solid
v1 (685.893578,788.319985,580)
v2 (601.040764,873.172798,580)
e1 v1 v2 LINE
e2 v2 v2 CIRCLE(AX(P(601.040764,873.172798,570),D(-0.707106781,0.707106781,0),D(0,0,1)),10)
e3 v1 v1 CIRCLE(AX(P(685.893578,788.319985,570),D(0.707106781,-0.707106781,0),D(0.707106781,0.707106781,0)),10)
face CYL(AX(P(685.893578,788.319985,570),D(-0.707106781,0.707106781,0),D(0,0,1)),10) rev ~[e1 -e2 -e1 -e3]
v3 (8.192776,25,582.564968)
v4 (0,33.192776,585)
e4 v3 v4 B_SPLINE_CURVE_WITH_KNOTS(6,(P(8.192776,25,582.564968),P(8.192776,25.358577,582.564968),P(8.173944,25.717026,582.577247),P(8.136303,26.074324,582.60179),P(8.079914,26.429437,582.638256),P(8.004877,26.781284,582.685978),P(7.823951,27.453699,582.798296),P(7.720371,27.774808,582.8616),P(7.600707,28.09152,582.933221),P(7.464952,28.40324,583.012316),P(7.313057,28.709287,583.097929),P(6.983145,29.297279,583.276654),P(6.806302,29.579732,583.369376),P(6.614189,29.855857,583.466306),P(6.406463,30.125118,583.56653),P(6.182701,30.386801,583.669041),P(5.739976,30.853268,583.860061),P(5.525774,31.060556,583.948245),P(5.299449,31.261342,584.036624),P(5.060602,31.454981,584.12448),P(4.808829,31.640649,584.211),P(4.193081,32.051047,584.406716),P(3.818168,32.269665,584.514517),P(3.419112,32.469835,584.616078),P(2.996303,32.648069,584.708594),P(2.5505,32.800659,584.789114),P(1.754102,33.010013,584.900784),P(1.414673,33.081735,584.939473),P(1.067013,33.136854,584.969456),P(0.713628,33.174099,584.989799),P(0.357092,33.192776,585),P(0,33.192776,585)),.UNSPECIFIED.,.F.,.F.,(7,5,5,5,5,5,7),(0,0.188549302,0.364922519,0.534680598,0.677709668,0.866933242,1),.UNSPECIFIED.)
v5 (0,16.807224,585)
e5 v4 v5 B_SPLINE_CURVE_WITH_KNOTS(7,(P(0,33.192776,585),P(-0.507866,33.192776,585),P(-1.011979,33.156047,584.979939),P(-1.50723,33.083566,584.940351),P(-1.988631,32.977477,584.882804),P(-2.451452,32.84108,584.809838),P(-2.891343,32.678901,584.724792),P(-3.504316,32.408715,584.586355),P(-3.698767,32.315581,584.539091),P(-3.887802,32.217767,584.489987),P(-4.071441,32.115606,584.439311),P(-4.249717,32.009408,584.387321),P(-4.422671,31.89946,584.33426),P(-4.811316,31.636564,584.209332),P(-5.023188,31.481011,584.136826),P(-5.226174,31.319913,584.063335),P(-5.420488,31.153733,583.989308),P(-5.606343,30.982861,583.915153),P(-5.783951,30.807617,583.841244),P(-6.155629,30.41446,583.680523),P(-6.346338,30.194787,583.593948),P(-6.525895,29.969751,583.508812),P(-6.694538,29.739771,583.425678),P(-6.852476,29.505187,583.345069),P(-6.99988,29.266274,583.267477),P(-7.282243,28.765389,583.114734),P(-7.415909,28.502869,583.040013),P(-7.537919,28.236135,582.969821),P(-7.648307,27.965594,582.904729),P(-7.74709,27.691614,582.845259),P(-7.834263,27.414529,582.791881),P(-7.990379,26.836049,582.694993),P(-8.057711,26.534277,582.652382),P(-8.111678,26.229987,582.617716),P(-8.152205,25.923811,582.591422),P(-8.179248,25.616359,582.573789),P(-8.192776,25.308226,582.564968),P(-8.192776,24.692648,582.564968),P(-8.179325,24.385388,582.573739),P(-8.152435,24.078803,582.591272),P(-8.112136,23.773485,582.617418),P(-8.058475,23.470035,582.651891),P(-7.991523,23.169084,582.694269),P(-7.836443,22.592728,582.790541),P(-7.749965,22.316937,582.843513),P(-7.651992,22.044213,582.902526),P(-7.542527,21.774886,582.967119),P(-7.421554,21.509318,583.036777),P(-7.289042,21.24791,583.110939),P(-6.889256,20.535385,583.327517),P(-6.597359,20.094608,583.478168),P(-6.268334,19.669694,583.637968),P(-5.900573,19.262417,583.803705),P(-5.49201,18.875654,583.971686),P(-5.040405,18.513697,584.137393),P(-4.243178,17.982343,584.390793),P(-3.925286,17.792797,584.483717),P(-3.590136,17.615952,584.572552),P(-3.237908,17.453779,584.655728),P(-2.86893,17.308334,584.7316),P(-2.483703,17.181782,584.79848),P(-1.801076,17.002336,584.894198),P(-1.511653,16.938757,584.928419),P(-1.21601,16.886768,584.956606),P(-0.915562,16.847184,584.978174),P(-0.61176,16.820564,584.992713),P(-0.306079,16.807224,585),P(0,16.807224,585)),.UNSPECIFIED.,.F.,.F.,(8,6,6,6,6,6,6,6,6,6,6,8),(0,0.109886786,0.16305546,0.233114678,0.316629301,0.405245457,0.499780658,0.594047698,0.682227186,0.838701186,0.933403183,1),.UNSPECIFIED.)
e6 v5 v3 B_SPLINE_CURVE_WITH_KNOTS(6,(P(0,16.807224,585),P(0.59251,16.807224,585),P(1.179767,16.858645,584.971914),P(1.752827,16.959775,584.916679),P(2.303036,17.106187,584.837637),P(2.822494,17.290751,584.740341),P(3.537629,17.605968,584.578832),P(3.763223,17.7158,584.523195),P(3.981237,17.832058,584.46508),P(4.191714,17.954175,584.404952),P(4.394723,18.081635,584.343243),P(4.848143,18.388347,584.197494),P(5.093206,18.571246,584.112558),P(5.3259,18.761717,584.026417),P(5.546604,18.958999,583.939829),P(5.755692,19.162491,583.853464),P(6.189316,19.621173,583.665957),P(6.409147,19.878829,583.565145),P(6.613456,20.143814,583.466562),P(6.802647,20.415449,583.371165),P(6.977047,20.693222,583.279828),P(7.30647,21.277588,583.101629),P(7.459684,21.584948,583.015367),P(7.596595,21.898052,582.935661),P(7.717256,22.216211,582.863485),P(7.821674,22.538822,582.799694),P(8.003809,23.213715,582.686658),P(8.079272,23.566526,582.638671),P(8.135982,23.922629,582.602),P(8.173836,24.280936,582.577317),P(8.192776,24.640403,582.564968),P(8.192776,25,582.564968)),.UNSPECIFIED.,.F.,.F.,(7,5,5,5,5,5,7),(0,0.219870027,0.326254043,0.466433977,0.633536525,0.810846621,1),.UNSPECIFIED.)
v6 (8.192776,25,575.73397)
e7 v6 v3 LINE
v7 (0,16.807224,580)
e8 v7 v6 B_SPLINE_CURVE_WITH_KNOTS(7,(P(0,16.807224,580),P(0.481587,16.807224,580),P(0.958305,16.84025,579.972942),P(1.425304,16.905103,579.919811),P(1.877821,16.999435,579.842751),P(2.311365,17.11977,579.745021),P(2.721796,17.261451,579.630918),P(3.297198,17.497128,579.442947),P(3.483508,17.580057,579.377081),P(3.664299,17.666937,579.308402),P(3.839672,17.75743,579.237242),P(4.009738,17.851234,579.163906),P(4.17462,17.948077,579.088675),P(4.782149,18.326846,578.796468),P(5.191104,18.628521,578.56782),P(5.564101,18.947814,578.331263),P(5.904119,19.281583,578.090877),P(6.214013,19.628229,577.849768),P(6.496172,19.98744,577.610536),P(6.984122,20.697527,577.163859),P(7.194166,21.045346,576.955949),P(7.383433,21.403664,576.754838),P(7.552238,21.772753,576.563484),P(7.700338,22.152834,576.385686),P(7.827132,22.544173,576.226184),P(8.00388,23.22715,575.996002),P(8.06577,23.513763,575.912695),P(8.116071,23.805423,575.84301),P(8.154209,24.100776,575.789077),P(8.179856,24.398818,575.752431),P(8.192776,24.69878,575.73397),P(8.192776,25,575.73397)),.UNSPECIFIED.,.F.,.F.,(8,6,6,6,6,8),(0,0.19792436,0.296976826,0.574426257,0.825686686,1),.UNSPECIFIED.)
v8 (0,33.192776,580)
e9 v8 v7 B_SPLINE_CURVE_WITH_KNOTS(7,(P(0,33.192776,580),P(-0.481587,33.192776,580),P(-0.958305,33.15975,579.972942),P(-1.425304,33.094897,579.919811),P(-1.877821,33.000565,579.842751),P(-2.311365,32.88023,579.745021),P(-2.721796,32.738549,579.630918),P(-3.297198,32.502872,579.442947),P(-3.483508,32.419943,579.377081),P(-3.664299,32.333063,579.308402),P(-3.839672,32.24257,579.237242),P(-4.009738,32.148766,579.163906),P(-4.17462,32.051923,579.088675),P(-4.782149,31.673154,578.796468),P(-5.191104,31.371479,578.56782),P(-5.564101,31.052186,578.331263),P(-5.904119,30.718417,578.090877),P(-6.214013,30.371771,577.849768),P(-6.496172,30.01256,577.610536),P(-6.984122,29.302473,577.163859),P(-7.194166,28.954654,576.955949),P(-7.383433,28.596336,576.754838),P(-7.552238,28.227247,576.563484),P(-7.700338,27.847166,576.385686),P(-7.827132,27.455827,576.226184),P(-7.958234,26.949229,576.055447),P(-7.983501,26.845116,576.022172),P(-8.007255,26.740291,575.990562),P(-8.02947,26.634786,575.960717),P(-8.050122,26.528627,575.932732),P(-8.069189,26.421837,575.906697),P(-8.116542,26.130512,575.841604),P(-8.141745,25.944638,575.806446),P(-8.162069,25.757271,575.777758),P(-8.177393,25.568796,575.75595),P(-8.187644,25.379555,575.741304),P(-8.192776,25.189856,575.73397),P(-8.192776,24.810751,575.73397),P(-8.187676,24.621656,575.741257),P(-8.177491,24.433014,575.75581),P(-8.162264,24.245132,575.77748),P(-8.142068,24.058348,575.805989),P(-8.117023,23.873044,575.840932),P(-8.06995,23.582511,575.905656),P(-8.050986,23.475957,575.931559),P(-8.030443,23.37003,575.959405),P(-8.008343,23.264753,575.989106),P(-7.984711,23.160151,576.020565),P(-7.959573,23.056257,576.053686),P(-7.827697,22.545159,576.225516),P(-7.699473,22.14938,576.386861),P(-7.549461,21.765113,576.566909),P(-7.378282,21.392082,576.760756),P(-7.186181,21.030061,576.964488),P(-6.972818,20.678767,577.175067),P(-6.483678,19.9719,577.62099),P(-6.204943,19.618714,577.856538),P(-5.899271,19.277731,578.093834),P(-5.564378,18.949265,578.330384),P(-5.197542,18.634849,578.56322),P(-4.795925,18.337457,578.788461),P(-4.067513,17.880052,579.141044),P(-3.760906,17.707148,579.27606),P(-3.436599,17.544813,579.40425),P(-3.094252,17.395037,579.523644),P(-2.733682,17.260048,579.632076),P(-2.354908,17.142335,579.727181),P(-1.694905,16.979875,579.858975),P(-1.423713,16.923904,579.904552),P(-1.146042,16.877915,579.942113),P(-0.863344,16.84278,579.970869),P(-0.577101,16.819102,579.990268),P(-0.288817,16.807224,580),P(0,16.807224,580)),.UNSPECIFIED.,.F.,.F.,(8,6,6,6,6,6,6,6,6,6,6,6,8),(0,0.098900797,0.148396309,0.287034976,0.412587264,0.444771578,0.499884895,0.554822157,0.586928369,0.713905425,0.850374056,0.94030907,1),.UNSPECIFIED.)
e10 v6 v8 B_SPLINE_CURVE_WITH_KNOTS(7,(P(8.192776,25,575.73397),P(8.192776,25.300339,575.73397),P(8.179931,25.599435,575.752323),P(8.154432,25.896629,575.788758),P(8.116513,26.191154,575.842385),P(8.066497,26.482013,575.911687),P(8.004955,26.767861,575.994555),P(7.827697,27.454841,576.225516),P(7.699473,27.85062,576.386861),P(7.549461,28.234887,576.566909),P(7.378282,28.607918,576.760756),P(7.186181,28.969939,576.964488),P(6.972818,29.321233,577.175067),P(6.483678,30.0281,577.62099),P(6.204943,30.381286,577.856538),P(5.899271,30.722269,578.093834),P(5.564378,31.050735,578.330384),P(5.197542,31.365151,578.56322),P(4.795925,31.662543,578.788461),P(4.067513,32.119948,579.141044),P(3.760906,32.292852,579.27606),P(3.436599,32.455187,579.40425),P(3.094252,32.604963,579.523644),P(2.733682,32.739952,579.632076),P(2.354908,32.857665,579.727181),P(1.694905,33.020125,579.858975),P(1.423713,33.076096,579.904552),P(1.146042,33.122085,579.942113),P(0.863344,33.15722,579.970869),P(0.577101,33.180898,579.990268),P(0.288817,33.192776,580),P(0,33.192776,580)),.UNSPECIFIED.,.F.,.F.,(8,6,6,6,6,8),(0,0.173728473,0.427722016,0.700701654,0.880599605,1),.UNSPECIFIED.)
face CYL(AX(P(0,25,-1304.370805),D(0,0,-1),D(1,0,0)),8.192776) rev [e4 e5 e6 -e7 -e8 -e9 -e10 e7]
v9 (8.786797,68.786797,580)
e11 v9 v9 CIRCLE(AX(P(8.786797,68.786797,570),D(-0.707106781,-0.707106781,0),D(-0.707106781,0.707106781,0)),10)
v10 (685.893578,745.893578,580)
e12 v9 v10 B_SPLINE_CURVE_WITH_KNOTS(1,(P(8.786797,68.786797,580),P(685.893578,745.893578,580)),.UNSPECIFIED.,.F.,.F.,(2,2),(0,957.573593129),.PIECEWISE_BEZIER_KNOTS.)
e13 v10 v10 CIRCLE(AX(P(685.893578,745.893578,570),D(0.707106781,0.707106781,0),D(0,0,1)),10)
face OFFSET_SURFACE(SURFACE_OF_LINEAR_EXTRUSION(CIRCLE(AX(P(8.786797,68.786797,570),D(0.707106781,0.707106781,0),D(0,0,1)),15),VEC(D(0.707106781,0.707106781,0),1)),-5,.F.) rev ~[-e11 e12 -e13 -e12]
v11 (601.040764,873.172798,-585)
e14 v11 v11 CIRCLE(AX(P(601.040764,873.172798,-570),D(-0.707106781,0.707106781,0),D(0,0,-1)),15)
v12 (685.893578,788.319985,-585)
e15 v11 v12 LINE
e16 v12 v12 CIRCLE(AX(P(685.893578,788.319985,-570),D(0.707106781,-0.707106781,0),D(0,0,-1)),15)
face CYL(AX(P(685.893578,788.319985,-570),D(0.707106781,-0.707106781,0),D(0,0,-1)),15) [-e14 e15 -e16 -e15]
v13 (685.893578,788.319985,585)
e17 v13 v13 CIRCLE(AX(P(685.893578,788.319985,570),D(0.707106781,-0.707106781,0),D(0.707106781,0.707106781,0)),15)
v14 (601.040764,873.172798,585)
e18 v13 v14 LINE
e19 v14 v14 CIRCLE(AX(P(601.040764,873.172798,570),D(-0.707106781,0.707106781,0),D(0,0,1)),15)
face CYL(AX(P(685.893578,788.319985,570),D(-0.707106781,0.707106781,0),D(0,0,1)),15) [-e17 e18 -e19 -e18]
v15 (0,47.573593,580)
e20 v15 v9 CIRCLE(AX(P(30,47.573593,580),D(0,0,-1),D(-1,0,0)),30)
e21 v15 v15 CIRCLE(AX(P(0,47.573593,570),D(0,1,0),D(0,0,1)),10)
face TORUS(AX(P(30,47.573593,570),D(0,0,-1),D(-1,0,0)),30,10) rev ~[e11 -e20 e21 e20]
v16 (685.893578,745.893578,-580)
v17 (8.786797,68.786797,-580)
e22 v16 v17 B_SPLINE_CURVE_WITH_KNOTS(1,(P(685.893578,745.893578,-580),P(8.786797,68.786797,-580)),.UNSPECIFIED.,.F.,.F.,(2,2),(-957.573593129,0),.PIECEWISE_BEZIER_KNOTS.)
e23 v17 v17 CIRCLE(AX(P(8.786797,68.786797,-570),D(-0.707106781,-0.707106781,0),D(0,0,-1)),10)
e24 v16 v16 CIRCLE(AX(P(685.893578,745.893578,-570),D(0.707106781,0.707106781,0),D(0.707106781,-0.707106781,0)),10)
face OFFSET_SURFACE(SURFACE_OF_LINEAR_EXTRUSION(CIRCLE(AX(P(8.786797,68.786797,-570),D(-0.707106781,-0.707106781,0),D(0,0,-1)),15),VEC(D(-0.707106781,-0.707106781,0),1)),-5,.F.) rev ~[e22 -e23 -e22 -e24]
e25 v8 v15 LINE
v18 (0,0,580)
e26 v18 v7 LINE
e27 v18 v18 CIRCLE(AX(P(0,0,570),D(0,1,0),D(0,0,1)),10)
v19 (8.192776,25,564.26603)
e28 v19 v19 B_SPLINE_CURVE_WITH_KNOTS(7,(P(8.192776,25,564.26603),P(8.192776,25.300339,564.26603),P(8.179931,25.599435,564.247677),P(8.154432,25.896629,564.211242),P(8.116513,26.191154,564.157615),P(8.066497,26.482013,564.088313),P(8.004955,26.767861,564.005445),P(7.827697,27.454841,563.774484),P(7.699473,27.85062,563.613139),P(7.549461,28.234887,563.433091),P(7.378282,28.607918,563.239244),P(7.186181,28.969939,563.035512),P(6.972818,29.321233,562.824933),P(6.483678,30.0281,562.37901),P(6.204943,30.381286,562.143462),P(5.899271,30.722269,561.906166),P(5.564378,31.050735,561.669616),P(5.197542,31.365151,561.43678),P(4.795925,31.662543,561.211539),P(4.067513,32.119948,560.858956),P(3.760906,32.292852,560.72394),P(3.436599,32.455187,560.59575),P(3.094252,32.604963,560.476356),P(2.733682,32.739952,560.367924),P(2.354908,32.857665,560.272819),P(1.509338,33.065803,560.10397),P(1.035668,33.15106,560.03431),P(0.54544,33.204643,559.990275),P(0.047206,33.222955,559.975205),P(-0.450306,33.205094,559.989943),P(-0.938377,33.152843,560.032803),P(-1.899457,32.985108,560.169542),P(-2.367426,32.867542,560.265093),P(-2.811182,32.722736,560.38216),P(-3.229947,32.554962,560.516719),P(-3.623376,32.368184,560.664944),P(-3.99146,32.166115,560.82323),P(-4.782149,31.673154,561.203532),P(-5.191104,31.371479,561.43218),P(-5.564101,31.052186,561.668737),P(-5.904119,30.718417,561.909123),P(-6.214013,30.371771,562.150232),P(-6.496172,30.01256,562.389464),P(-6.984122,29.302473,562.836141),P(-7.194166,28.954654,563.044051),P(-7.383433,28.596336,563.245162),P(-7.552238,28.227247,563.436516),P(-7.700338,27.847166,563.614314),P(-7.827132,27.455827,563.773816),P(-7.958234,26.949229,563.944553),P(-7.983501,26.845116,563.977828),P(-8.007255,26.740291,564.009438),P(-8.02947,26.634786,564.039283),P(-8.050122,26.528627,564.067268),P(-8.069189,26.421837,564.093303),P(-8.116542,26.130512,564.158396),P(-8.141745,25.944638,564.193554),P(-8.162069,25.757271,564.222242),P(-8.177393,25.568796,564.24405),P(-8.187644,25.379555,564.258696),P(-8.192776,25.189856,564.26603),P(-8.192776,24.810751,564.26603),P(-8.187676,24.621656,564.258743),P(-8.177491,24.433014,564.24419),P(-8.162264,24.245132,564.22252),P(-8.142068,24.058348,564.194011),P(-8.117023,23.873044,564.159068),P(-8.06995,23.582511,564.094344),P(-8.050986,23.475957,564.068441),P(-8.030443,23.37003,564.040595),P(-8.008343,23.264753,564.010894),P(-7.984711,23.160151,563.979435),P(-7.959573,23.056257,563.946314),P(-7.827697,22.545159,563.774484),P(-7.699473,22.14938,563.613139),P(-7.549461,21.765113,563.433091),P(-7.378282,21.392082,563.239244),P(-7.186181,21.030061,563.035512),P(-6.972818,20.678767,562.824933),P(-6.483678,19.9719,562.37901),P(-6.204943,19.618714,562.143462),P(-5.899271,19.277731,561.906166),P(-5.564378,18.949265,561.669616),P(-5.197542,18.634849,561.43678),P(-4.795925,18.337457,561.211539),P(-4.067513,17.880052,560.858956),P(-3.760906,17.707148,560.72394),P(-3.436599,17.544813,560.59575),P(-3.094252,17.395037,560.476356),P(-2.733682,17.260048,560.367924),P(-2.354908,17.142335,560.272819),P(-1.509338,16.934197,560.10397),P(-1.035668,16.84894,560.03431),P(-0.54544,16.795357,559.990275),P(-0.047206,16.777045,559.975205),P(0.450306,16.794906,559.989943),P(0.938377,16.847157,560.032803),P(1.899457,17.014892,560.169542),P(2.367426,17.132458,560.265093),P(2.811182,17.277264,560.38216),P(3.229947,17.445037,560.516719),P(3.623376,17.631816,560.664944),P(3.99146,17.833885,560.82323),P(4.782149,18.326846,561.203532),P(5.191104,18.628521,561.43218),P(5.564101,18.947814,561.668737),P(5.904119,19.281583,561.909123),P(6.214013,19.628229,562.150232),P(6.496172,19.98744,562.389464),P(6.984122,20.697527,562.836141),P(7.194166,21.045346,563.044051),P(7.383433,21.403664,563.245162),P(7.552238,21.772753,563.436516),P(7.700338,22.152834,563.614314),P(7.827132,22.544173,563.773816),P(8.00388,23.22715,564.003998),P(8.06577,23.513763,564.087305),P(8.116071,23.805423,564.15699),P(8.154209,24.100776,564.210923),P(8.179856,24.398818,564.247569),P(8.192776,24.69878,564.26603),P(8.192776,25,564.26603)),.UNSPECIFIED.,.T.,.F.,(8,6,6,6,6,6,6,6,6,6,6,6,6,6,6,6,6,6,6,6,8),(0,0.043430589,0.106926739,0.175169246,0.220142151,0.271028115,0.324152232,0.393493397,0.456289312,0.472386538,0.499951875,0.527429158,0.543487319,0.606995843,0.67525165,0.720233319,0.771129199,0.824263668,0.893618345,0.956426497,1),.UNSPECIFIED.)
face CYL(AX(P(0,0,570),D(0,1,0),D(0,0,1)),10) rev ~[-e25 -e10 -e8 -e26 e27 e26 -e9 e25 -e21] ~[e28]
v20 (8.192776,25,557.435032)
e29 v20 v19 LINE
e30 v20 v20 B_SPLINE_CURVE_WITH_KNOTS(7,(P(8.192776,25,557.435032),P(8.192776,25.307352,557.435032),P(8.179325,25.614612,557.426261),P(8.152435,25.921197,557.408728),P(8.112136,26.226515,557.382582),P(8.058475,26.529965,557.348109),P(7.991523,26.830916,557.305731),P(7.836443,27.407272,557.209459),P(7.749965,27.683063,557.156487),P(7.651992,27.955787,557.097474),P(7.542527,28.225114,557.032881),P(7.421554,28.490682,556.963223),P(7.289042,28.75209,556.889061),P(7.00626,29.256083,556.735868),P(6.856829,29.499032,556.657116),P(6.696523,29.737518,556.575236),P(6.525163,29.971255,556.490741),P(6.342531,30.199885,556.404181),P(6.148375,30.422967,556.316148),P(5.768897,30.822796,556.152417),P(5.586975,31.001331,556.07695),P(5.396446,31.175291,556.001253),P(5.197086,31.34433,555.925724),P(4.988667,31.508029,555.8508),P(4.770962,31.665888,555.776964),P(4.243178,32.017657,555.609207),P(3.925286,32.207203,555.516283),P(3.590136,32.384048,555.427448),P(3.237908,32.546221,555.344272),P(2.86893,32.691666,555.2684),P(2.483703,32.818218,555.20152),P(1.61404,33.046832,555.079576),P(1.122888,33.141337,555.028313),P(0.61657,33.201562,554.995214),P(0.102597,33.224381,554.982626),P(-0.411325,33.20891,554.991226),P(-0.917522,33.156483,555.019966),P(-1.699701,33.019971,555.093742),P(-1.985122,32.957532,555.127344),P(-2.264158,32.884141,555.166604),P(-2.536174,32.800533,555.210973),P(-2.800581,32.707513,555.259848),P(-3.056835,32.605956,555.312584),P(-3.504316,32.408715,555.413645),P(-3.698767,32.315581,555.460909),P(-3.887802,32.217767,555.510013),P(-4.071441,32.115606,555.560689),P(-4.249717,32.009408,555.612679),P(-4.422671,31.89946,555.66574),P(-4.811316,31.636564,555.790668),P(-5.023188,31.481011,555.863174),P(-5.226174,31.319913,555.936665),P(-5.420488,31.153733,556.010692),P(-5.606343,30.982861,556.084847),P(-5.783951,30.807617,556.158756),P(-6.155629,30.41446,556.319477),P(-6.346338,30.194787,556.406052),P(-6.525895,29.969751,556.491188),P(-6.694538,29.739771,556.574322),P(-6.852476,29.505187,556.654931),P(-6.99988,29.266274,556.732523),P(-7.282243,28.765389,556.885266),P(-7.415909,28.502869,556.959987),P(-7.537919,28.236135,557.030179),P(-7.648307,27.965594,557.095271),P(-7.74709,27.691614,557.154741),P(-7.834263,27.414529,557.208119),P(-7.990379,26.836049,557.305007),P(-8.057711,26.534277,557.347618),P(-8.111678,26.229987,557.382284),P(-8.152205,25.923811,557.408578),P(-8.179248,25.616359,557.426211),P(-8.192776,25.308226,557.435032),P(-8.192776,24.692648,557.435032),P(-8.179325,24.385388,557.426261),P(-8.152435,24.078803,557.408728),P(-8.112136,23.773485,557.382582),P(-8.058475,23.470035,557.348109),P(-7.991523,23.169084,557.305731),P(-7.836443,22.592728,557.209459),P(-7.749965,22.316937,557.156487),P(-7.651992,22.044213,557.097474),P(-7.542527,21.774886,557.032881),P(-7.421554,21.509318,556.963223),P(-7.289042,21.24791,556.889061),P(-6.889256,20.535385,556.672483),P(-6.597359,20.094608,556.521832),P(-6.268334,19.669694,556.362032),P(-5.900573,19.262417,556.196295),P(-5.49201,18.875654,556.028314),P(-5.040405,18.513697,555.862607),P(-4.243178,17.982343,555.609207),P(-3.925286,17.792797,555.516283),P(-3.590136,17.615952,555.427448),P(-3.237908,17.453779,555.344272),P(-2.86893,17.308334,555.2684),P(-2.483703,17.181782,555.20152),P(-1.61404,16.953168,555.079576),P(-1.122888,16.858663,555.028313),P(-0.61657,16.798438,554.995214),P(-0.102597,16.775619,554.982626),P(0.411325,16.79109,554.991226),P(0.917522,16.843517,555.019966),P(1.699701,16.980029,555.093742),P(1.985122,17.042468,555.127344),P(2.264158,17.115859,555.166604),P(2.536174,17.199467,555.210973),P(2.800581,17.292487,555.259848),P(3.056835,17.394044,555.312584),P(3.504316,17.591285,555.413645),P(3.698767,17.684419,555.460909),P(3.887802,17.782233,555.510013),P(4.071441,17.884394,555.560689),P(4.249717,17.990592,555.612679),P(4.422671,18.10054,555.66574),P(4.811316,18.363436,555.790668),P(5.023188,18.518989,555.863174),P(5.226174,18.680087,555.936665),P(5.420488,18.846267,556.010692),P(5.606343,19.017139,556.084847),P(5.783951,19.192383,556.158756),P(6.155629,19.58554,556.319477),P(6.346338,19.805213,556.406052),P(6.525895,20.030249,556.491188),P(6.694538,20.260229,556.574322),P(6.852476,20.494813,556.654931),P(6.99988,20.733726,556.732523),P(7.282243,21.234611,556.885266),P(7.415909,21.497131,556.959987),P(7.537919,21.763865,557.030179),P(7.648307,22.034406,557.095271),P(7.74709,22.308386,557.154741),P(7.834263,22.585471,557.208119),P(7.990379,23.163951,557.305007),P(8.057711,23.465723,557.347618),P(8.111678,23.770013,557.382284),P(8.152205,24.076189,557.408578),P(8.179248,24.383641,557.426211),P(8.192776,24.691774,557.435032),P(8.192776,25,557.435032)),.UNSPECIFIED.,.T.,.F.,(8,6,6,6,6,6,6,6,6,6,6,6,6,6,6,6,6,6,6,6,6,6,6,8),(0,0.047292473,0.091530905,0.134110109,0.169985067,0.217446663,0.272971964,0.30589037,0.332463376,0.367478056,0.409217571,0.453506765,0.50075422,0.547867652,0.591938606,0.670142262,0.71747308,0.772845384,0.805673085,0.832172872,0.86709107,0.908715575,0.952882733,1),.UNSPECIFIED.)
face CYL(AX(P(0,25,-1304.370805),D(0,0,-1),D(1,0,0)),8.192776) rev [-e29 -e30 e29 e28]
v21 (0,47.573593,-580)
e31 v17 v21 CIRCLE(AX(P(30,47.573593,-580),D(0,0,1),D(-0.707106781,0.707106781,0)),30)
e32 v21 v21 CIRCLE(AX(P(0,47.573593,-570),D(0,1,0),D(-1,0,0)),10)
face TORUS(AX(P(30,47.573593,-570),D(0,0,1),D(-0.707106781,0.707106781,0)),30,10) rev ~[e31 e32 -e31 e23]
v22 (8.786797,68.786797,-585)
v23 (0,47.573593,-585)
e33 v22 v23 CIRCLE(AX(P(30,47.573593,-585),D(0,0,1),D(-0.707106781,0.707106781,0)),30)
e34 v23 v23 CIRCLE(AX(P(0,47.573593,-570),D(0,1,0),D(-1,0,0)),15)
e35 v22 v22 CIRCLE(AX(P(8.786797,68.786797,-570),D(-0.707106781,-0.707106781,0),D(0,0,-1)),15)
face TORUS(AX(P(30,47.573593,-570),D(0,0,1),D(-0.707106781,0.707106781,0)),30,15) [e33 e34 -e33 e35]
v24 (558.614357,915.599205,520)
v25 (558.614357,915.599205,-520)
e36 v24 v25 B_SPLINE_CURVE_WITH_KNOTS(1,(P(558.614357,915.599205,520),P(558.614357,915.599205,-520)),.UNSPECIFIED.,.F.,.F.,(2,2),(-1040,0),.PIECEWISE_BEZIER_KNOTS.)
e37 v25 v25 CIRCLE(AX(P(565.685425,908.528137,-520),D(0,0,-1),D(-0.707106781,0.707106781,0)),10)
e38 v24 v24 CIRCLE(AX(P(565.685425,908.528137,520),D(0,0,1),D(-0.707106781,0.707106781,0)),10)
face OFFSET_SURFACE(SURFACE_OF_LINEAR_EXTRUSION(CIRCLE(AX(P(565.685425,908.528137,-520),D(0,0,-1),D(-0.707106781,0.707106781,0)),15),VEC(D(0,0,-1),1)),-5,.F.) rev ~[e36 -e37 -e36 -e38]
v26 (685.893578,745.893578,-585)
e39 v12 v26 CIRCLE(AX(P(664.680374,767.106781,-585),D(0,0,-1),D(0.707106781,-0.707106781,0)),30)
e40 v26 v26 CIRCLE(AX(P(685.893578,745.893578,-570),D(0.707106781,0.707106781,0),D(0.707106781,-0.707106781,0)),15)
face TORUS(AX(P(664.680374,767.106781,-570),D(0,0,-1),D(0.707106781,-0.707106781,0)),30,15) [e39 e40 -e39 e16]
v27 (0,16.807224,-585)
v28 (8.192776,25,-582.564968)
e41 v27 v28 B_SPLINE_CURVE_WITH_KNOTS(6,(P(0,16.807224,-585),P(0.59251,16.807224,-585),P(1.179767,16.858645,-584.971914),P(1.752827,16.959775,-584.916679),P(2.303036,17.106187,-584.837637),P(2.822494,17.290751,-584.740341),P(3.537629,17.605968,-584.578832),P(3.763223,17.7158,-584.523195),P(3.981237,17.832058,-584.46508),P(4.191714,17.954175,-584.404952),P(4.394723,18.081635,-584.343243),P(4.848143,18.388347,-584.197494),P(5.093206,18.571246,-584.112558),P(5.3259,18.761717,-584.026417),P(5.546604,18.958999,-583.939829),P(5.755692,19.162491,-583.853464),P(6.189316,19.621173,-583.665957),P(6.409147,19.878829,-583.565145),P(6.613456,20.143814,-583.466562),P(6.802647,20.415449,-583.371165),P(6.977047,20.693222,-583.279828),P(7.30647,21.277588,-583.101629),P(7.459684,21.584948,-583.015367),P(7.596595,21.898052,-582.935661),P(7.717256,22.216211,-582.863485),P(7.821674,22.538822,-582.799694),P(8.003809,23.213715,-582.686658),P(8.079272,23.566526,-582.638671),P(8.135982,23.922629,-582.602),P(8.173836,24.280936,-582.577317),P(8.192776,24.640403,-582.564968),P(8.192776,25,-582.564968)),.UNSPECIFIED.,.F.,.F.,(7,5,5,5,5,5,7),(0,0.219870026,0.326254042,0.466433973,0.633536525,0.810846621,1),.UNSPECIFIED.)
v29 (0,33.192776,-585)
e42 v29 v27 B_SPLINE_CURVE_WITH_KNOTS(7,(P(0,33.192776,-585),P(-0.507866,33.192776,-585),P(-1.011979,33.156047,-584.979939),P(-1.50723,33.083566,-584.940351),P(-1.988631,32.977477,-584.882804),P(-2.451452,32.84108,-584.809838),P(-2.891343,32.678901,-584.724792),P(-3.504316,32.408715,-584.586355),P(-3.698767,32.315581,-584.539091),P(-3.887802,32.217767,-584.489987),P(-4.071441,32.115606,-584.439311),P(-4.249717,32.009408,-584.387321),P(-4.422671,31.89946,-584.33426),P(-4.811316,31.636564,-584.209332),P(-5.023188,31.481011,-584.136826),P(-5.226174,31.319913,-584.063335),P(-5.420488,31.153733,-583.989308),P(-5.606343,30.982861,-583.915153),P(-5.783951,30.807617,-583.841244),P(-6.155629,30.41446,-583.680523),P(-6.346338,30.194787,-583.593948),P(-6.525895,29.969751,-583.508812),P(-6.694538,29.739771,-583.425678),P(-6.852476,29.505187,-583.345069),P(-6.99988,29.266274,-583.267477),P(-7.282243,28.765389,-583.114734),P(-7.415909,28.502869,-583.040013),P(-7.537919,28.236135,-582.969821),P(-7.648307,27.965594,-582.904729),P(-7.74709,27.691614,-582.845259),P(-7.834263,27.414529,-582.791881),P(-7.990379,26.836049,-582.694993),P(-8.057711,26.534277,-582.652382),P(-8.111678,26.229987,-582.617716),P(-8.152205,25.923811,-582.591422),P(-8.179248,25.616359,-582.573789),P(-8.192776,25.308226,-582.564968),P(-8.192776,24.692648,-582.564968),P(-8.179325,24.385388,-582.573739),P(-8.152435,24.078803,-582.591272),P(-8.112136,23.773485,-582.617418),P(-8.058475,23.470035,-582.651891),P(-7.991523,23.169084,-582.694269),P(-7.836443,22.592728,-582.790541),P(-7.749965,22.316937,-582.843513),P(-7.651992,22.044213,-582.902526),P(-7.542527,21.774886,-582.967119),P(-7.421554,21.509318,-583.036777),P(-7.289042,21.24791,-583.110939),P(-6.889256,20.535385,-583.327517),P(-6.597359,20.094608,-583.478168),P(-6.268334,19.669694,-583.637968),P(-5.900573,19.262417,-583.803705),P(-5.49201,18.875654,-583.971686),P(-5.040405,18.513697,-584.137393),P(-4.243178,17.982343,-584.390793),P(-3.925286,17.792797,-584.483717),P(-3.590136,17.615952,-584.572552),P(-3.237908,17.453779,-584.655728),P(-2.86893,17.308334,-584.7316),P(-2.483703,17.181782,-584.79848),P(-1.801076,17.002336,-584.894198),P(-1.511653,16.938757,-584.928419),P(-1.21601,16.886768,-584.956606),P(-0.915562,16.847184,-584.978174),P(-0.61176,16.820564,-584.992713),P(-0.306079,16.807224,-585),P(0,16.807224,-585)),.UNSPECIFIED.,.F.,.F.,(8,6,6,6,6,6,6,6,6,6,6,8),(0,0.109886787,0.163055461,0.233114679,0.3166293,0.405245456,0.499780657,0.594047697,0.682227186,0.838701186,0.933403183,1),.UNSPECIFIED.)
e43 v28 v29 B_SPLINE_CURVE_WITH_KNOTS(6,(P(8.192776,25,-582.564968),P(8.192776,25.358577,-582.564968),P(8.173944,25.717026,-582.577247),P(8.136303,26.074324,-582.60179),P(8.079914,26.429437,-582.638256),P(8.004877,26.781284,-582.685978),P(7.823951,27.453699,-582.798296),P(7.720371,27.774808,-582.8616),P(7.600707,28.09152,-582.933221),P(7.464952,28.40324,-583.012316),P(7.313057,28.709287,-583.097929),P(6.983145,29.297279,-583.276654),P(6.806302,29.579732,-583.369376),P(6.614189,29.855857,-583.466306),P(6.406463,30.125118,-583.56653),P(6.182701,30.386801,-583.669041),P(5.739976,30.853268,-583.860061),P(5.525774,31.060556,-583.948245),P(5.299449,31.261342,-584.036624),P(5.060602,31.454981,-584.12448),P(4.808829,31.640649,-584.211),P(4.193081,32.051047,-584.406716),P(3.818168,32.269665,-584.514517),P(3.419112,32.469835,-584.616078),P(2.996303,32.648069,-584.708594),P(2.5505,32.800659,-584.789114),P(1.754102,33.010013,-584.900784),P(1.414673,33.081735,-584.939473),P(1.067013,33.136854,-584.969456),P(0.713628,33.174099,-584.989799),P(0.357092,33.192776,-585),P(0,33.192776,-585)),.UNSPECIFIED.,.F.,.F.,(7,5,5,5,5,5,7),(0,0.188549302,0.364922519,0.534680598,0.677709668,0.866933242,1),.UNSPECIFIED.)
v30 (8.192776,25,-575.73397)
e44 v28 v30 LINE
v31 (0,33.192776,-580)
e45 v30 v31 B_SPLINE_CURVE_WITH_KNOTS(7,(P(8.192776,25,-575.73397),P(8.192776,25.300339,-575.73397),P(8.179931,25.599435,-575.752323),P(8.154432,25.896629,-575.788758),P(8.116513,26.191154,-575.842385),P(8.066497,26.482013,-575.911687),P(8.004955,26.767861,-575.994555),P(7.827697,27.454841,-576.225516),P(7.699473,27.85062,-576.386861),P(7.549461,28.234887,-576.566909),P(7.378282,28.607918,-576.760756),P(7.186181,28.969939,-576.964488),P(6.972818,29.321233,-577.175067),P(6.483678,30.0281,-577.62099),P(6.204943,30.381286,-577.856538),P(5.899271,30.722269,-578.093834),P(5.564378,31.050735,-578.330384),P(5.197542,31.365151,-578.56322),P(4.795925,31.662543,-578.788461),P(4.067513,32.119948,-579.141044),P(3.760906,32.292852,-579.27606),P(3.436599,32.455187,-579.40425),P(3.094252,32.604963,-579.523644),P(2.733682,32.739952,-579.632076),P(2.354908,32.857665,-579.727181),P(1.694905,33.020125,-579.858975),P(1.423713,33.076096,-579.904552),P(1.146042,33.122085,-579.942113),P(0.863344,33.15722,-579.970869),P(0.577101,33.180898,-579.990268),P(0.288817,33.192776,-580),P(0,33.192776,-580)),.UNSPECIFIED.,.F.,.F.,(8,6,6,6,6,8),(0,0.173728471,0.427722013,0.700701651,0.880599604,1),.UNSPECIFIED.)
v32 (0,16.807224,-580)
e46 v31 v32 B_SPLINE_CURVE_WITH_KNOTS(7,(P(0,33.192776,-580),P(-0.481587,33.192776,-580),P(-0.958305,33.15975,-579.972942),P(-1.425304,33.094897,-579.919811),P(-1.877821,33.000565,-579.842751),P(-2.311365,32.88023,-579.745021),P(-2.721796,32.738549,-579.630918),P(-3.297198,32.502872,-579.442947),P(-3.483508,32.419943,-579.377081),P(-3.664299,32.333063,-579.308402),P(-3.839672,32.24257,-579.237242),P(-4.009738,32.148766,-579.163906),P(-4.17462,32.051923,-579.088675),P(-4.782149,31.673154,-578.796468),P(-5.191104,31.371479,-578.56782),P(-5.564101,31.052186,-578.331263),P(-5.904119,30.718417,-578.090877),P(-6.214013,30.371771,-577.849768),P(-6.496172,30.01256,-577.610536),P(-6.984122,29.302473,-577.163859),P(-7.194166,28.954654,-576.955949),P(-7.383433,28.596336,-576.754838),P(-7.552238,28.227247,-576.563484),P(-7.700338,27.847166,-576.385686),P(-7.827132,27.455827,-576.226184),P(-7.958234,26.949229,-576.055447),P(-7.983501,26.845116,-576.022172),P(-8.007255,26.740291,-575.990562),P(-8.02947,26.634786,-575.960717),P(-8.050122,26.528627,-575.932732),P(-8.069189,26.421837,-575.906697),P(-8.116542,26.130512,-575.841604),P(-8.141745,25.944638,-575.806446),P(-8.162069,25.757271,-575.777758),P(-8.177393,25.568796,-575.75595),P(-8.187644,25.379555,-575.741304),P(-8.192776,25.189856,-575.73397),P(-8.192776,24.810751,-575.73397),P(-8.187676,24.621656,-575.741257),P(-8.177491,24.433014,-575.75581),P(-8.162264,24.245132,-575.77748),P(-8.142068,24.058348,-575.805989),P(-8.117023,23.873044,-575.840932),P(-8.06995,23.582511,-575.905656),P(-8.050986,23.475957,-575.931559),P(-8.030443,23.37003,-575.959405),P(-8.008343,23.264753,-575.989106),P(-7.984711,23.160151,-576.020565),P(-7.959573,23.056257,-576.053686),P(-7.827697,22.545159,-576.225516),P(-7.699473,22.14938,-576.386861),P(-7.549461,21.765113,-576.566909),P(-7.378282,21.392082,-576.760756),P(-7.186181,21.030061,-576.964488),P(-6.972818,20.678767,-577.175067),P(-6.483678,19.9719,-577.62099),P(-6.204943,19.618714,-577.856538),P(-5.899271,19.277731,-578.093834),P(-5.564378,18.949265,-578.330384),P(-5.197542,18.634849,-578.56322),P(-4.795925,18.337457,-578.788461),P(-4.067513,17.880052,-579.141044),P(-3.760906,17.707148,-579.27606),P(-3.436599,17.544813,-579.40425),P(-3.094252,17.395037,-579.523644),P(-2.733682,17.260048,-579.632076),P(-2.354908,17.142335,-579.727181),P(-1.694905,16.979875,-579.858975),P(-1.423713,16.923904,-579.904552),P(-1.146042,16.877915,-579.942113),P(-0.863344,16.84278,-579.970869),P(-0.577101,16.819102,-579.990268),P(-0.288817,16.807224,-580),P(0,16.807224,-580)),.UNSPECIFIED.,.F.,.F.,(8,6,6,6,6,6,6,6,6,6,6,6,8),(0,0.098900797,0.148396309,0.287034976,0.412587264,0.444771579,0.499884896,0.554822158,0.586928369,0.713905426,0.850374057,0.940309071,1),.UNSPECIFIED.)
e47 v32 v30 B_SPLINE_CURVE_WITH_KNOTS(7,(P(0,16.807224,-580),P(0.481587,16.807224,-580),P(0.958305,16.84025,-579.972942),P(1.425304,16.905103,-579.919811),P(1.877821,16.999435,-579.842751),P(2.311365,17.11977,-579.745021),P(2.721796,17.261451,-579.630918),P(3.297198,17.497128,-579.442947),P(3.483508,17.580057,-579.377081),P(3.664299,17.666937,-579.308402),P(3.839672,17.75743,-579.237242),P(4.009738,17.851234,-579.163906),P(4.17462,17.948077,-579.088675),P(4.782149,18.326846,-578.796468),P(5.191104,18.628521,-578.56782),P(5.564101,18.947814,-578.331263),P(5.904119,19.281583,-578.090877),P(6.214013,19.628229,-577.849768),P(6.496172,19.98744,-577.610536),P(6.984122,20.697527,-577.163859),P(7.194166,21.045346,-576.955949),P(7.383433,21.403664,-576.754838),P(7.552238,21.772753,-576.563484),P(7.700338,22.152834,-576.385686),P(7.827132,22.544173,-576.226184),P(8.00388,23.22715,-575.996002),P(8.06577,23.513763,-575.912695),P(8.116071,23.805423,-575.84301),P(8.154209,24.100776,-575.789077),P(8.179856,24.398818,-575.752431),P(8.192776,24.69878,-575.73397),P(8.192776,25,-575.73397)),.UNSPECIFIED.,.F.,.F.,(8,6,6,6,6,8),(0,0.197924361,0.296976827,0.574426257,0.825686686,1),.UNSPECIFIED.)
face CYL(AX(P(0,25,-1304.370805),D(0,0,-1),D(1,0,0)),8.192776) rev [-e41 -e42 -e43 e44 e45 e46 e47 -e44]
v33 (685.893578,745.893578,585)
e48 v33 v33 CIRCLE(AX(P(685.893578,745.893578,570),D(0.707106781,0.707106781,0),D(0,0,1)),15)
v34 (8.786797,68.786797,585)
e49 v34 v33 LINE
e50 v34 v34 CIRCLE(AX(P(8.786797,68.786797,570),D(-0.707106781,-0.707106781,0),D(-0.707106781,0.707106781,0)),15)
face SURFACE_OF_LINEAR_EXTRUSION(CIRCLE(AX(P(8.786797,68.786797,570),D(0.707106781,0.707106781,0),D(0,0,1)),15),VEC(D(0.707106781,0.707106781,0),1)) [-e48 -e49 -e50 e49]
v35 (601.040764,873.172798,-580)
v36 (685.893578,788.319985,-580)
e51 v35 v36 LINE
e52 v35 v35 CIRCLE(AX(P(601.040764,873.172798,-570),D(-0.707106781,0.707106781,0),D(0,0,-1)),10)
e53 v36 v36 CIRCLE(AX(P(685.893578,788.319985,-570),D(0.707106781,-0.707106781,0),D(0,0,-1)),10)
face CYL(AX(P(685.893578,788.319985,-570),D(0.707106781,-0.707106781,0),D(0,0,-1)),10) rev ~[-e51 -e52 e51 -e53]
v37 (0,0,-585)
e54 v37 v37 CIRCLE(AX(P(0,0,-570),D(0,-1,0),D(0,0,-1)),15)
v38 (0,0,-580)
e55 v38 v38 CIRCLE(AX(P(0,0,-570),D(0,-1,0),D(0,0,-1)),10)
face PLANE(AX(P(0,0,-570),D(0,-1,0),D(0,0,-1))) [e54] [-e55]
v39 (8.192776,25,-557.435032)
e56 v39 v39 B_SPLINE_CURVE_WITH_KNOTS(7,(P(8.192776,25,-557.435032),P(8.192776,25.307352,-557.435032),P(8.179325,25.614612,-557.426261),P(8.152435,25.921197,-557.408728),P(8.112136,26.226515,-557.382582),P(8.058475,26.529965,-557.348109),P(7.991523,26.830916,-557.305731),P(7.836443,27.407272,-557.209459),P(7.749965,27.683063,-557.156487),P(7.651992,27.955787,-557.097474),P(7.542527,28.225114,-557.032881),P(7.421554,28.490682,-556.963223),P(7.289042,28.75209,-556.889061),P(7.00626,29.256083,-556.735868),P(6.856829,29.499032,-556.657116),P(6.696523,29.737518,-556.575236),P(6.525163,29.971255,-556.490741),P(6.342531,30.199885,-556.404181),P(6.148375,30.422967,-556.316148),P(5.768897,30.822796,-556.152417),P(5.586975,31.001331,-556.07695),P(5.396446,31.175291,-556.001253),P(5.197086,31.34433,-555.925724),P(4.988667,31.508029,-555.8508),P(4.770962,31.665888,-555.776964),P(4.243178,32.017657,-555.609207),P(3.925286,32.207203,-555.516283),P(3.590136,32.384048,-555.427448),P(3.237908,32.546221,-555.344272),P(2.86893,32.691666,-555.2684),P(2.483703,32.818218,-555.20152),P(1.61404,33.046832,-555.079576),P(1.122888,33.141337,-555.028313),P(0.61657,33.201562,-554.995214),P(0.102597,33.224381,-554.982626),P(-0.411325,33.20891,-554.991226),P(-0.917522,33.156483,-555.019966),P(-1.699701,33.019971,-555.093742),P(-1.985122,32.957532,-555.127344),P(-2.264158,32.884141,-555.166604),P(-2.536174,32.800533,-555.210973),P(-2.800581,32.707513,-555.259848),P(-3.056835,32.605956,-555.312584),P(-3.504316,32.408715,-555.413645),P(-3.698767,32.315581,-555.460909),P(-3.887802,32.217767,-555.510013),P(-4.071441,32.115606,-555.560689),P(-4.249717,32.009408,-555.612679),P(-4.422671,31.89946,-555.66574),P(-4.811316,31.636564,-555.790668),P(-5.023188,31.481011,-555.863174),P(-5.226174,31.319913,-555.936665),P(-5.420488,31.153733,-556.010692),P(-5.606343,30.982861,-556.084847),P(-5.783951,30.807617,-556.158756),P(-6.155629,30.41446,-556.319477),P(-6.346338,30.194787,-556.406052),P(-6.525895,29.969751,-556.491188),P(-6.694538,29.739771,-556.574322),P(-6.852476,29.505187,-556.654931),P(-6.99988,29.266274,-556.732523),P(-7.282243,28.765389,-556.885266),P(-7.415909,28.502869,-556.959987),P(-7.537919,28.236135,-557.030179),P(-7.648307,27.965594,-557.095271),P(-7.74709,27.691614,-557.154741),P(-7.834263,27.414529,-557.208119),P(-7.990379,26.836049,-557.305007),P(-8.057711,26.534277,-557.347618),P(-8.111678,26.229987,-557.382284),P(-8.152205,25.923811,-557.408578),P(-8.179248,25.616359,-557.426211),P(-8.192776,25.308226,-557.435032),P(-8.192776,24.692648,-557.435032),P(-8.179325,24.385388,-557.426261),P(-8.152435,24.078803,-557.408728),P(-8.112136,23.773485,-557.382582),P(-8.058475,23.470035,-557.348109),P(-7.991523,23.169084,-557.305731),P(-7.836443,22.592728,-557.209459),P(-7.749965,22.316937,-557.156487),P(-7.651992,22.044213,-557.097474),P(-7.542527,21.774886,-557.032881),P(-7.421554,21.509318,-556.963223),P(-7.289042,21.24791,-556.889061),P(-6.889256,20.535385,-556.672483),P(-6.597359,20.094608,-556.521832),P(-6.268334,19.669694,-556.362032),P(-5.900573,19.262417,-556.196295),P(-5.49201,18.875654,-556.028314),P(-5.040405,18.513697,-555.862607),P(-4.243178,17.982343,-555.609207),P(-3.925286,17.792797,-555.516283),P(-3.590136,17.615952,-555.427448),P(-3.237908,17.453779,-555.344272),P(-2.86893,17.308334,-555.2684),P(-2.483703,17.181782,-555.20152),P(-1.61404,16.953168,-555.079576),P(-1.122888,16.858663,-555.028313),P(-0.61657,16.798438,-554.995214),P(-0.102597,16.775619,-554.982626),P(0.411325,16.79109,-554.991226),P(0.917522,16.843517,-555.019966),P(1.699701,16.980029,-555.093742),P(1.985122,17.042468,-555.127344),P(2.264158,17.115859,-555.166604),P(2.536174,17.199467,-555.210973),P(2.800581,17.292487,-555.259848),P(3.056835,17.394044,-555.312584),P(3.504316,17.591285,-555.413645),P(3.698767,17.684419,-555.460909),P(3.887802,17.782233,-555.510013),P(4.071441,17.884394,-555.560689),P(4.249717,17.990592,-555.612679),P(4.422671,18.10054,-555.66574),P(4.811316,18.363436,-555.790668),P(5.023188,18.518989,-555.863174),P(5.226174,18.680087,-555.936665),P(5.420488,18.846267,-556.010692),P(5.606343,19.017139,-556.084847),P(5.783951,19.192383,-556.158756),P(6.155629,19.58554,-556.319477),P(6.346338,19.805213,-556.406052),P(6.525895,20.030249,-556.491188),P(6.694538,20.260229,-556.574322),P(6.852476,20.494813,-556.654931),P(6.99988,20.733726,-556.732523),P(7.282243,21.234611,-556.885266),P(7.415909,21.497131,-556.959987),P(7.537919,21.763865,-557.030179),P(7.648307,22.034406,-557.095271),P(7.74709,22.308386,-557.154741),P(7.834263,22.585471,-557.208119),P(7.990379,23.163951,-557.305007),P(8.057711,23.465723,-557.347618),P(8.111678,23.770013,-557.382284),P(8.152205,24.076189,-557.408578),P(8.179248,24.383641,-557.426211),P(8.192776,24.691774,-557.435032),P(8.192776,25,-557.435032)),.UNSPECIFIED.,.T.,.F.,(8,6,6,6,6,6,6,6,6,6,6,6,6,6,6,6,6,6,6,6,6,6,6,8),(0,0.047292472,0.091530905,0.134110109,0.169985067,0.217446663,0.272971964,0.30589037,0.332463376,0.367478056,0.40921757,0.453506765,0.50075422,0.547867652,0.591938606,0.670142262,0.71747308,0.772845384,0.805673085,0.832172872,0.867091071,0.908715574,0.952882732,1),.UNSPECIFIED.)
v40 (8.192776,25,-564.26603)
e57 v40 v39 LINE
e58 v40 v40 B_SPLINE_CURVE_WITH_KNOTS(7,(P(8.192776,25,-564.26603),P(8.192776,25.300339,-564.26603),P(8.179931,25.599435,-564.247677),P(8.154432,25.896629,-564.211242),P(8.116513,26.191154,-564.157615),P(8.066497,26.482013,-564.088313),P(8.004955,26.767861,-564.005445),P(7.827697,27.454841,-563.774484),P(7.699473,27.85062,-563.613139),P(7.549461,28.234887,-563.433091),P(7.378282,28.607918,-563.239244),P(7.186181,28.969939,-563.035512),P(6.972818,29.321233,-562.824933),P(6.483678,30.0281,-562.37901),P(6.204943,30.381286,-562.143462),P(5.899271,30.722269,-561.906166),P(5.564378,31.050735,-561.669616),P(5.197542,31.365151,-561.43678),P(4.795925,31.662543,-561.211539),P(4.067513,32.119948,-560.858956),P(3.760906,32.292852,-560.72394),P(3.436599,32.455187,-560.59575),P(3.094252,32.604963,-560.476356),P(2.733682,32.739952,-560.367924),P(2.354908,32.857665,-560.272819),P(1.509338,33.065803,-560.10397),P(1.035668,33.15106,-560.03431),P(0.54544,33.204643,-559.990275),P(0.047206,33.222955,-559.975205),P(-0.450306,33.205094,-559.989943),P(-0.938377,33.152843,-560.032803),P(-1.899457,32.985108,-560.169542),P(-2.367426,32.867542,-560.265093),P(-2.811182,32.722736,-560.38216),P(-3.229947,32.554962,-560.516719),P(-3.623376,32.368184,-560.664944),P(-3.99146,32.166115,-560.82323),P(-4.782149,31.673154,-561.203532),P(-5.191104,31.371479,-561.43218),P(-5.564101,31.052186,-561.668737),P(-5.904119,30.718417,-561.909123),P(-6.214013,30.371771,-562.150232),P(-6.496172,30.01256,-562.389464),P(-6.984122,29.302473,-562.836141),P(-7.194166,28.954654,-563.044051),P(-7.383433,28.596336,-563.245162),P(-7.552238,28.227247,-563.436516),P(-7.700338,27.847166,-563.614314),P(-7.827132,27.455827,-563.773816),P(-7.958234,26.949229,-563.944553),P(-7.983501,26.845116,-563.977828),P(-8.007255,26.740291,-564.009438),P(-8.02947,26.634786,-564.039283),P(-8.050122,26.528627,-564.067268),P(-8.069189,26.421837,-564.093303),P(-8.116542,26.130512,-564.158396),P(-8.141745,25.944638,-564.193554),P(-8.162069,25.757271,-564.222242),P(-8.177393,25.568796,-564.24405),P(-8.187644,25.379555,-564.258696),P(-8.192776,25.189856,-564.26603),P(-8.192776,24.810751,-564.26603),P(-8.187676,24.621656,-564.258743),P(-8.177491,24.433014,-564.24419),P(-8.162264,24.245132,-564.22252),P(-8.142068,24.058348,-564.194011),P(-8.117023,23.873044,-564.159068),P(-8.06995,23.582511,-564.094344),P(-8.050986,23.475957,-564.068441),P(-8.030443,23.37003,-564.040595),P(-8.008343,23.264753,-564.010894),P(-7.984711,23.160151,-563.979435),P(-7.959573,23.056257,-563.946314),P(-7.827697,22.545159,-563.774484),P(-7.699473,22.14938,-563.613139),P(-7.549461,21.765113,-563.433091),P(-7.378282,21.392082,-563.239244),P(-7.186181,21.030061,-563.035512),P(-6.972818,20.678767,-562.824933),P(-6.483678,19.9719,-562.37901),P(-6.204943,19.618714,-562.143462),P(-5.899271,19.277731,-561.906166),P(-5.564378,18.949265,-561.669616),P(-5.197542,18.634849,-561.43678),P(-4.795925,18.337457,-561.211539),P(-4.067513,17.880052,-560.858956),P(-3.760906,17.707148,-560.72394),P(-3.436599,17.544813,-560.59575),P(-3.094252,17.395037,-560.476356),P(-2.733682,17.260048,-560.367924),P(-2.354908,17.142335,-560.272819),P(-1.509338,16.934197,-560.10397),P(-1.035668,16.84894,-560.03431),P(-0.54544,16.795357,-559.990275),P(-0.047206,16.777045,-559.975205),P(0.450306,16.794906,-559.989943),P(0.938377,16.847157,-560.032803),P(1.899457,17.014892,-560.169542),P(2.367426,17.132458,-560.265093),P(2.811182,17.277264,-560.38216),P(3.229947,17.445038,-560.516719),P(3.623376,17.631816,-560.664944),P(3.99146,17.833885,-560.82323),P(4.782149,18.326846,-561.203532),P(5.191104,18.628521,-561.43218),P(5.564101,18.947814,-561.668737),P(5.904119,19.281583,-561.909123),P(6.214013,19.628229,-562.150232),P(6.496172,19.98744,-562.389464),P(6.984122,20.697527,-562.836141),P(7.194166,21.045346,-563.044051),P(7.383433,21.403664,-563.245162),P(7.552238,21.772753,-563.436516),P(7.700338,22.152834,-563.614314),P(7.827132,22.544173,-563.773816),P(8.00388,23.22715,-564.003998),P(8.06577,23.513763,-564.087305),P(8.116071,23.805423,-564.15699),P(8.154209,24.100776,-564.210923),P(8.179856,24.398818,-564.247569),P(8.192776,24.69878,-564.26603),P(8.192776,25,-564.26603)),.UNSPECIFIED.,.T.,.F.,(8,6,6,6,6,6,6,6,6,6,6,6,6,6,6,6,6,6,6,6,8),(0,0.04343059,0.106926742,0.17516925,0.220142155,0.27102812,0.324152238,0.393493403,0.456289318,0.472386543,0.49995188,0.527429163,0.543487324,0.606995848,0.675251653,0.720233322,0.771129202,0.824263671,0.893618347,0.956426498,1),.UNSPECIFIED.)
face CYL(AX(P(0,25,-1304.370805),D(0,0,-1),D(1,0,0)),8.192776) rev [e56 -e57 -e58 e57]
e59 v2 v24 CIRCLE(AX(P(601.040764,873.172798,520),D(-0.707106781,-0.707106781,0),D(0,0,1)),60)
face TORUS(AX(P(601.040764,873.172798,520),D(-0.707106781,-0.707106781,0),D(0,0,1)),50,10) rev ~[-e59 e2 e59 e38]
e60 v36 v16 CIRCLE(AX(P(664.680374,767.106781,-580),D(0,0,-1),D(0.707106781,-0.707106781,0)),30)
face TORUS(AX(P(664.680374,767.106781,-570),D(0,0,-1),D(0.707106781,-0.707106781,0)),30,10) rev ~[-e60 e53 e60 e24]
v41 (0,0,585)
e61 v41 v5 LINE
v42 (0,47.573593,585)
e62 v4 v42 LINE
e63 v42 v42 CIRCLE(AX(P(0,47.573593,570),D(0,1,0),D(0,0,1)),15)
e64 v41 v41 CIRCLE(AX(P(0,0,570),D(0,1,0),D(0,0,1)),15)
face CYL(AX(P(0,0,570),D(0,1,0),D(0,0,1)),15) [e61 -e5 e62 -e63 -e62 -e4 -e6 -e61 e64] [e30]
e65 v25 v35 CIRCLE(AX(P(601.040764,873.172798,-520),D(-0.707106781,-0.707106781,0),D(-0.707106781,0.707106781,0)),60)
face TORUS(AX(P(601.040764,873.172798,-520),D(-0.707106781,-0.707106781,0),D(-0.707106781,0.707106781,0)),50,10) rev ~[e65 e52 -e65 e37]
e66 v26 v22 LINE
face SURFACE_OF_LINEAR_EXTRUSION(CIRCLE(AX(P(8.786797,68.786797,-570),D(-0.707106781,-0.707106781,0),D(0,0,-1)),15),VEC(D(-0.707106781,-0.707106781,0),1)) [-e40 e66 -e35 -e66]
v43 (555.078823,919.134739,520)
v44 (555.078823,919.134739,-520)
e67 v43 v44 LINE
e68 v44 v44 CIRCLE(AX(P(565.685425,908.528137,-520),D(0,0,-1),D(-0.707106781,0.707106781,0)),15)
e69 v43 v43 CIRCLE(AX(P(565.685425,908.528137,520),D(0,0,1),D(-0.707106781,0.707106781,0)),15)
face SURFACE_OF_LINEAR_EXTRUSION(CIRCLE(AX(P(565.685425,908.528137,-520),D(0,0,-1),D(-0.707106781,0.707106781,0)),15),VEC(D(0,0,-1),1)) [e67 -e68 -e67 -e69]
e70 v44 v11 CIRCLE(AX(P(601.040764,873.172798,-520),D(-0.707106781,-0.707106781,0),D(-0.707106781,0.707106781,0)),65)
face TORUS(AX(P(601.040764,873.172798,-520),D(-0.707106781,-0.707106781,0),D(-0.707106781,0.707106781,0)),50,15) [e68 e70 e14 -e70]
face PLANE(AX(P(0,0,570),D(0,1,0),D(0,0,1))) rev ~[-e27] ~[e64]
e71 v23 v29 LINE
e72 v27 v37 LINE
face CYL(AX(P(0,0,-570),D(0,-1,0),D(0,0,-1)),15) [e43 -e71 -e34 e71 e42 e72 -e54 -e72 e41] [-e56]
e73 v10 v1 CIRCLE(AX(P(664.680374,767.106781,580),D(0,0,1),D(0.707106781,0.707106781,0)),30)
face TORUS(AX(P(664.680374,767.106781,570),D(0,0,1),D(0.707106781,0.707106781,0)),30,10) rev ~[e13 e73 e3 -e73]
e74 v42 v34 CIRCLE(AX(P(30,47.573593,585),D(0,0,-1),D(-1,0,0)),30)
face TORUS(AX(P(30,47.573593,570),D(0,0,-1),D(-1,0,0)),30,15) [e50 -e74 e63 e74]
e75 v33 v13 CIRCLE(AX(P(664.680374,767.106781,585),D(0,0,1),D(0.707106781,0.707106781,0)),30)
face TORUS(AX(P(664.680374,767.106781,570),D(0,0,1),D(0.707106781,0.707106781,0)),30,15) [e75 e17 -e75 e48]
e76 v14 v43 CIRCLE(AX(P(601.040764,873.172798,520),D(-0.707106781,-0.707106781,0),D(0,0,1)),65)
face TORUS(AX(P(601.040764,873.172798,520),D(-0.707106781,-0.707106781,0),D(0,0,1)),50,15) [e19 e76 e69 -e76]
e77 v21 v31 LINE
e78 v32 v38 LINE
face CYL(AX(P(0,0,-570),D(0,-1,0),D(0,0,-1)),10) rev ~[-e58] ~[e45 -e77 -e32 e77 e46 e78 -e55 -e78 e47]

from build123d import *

# Parameters (mm, degrees)
SWEEP1_PROFILE_R        = 15
SHELL1_T                = -5
CUT_EXTRUDE1_DEPTH      = 1304.370804777
CUT_EXTRUDE1_DEPTH_BACK = 1304.370804777
SKETCH4_R               = 8.192776497


with BuildPart() as part:
    # Sweep1: sweep along a curve in space
    with BuildLine() as sweep1_path:
        Line((0, 0, 570), (0, 47.573593129, 570))
        ThreePointArc((0, 47.573593129, 570), (2.283614025, 59.0540961, 570), (8.786796564, 68.786796564, 570))
        Line((8.786796564, 68.786796564, 570), (685.893577751, 745.893577751, 570))
        ThreePointArc((685.893577751, 788.319984622, 570), (694.680374315, 767.106781187, 570), (685.893577751, 745.893577751, 570))
        Line((685.893577751, 788.319984622, 570), (601.040764009, 873.172798365, 570))
        ThreePointArc((601.040764009, 873.172798365, 570), (576.040764009, 898.172798365, 555.355339059), (565.685424949, 908.528137424, 520))
        Line((565.685424949, 908.528137424, -520), (565.685424949, 908.528137424, 520))
        ThreePointArc((565.685424949, 908.528137424, -520), (576.040764009, 898.172798365, -555.355339059), (601.040764009, 873.172798365, -570))
        Line((685.893577751, 788.319984622, -570), (601.040764009, 873.172798365, -570))
        ThreePointArc((685.893577751, 745.893577751, -570), (694.680374315, 767.106781187, -570), (685.893577751, 788.319984622, -570))
        Line((8.786796564, 68.786796564, -570), (685.893577751, 745.893577751, -570))
        ThreePointArc((8.786796564, 68.786796564, -570), (2.283614025, 59.0540961, -570), (0, 47.573593129, -570))
        Line((0, 0, -570), (0, 47.573593129, -570))
    # Sweep1 profile (on start of the path) → Sweep1 (sweep)
    with BuildSketch(Plane(origin=(0, 0, 570), x_dir=(0, 0, 1), z_dir=(0, 1, 0))):
        Circle(SWEEP1_PROFILE_R)
    sweep(path=sweep1_path.line)

    # Shell1
    shell1_openings = [part.faces().sort_by_distance(p)[0] for p in [
        (0, 0, 570),
        (0, 0, -570),
    ]]
    offset(amount=SHELL1_T, openings=shell1_openings, kind=Kind.INTERSECTION)

    # Sketch4 → Cut-Extrude1 (cut, two sides: drawn at the far end of the back side and taken through both)
    with BuildSketch(Plane.XY.offset(-CUT_EXTRUDE1_DEPTH_BACK)):
        with Locations((0, 25)):
            Circle(SKETCH4_R)
    extrude(amount=CUT_EXTRUDE1_DEPTH + CUT_EXTRUDE1_DEPTH_BACK, mode=Mode.SUBTRACT)


solid = part.part
